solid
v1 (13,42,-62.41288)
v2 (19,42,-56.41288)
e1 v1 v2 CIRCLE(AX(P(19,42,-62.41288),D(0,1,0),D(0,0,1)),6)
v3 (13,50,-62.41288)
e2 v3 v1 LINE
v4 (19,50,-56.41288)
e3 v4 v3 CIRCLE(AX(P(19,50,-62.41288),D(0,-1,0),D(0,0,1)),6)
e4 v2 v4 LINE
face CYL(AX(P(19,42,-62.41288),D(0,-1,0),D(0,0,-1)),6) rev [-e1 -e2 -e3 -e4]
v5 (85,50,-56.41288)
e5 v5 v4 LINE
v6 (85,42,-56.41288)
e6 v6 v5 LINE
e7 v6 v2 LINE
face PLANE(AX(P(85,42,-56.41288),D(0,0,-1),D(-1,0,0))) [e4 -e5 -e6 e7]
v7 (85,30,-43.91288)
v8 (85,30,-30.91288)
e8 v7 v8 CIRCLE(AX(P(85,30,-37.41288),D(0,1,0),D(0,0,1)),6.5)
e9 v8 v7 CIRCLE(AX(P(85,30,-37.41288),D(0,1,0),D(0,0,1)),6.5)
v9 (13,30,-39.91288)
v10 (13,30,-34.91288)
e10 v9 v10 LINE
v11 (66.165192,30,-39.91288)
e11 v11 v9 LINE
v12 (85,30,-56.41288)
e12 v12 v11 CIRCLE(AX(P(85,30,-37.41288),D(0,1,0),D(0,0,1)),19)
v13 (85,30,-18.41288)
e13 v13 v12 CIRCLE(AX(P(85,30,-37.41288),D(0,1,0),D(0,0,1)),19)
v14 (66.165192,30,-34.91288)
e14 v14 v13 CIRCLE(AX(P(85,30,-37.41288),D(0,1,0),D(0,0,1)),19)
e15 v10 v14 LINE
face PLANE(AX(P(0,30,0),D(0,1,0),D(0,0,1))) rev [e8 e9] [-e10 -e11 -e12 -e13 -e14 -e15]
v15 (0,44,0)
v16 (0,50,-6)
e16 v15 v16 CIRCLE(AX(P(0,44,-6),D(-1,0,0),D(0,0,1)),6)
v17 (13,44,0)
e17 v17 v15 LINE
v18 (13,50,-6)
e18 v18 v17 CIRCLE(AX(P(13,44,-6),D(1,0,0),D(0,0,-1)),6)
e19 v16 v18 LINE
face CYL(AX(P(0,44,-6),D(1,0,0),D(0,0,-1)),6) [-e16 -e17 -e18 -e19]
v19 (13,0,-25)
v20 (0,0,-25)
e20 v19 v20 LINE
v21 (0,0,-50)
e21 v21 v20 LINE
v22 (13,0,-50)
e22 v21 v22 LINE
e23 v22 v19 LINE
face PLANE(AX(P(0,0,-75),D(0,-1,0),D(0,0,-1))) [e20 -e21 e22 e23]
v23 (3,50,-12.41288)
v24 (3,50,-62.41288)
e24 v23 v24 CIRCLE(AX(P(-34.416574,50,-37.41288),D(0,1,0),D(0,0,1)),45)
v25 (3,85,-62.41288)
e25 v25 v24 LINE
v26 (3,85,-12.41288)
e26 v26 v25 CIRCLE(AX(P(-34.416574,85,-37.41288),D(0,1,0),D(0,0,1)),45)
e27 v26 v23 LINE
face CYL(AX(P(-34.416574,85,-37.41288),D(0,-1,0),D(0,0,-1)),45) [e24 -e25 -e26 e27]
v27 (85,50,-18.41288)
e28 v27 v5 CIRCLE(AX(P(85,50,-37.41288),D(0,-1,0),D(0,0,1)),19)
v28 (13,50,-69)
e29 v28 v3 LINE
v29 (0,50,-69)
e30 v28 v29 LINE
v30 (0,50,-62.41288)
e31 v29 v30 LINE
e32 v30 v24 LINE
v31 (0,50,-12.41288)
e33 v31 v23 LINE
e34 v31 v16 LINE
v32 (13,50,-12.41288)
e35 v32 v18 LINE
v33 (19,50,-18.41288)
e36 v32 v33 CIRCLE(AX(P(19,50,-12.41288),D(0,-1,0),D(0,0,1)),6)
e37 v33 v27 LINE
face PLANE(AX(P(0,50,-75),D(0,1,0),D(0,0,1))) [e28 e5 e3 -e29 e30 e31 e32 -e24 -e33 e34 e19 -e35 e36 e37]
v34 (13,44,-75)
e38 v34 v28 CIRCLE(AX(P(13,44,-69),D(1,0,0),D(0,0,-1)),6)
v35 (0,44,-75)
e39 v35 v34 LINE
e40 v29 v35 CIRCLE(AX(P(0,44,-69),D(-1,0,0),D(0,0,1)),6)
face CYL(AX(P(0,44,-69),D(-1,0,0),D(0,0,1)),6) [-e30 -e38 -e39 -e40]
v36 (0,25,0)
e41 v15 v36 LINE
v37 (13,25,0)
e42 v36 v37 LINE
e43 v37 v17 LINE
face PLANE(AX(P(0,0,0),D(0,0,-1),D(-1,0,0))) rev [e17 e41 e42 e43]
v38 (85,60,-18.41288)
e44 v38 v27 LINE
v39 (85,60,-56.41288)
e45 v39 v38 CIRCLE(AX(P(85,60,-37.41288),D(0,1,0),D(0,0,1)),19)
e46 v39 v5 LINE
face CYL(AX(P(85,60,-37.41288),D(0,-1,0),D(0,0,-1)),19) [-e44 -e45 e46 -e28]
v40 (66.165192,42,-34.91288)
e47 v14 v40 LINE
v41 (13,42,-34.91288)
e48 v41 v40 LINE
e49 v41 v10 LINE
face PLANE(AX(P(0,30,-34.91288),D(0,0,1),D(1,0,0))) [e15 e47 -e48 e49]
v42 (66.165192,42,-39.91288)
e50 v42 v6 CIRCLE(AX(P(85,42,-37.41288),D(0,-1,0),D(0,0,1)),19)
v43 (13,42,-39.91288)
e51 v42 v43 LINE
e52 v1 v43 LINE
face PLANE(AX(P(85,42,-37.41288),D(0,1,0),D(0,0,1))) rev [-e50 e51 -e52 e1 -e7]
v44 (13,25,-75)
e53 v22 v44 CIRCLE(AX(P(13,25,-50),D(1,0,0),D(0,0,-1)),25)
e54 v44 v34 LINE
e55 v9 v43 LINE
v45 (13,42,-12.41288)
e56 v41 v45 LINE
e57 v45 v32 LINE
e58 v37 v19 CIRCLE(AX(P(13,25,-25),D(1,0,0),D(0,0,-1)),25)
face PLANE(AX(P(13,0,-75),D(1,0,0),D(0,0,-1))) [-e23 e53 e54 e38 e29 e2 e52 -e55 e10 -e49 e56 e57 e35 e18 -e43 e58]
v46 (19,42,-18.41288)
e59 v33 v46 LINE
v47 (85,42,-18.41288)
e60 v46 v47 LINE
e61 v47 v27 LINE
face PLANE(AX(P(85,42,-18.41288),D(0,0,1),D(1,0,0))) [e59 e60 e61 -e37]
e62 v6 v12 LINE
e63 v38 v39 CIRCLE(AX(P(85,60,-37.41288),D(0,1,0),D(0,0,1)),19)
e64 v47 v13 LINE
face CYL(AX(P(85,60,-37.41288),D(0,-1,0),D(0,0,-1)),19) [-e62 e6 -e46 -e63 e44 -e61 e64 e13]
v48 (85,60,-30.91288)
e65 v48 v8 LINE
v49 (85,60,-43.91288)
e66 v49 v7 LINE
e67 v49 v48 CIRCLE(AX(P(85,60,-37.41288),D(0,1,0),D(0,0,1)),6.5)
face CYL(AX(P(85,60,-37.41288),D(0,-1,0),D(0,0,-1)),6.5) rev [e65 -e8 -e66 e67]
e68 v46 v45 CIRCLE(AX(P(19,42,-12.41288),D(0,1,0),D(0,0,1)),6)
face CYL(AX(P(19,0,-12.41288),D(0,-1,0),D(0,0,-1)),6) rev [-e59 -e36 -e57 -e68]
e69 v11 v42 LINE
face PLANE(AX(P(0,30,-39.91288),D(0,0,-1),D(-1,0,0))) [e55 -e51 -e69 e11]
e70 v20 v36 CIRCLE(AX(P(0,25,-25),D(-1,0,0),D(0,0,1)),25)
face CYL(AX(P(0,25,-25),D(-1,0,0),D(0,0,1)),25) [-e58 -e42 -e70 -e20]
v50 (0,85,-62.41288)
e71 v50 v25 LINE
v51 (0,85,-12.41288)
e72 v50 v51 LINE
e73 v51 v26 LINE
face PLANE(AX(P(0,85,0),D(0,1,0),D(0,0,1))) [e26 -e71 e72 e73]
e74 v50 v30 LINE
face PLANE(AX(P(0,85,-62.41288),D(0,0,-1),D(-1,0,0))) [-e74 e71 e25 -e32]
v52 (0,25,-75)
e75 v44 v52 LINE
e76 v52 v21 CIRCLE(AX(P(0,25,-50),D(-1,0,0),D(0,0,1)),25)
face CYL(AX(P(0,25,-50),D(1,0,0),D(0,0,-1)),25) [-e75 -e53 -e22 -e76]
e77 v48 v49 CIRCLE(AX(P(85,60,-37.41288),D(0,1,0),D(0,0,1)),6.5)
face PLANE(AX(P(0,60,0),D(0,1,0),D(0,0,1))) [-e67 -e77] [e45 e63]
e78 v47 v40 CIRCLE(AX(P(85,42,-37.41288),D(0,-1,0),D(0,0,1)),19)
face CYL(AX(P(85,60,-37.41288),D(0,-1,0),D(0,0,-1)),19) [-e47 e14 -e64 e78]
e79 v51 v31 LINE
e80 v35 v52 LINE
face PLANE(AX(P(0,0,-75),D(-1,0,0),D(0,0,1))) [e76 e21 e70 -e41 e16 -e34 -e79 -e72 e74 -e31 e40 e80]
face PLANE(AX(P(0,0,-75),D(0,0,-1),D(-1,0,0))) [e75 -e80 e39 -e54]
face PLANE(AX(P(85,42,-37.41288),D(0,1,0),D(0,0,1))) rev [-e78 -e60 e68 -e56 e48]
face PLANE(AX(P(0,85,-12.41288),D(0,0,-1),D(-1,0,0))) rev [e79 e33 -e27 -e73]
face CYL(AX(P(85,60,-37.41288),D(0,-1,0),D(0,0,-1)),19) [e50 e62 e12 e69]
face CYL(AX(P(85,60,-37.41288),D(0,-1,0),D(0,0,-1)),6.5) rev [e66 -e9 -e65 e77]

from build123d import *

# Parameters (mm, degrees)
BASE_BLOCK_SKETCH_W   = 13
BASE_BLOCK_SKETCH_H   = 50
BASE_BLOCK_DEPTH      = 75
BASE_END_ROUND_R25_R  = 25
BASE_EDGE_FILLET_R6_R = 6
ARM_WEB_DEPTH         = 35
HUB_BOSS_SKETCH_R     = 19
HUB_BOSS_SKETCH_R_2   = 6.5
HUB_BOSS_DEPTH        = 30
UPPER_LUG_DEPTH       = 8
CURVED_START          = -20
CURVED_BLADE_DEPTH    = 20
LUG_FILLET_R6_A_R     = 6
LUG_FILLET_R6_B_R     = 6


with BuildPart() as part:
    # Base Block Sketch → Base Block (new body)
    with BuildSketch(Plane.XY):
        with Locations((6.5, 25)):
            Rectangle(BASE_BLOCK_SKETCH_W, BASE_BLOCK_SKETCH_H)
    extrude(amount=-BASE_BLOCK_DEPTH)

    # Base End Round R25
    base_end_round_r25_edges = [part.edges().sort_by_distance(p)[0] for p in [
        (6.5, 0, 0),
        (6.5, 0, -75),
    ]]
    fillet(base_end_round_r25_edges, radius=BASE_END_ROUND_R25_R)

    # Base Edge Fillet R6
    base_edge_fillet_r6_edges = [part.edges().sort_by_distance(p)[0] for p in [
        (6.5, 50, -75),
        (6.5, 50, 0),
    ]]
    fillet(base_edge_fillet_r6_edges, radius=BASE_EDGE_FILLET_R6_R)

    # Arm Web Sketch → Arm Web (add)
    with BuildSketch(Plane(origin=(0, 50, 0), x_dir=(1, 0, 0), z_dir=(0, 1, 0))):
        with BuildLine():
            Line((3, 62.41287987), (0, 62.41287987))
            Line((0, 62.41287987), (0, 37.41287987))
            Line((0, 37.41287987), (0, 12.41287987))
            Line((0, 12.41287987), (3, 12.41287987))
            ThreePointArc((3, 12.41287987), (10.583426132, 37.41287987), (3, 62.41287987))
        make_face()
    extrude(amount=ARM_WEB_DEPTH)



with BuildPart() as body_2:
    # Hub Boss Sketch → Hub Boss (new body)
    with BuildSketch(Plane(origin=(0, 30, 0), x_dir=(1, 0, 0), z_dir=(0, 1, 0))):
        with Locations(Location((85, 37.41287987, 0), (0, 0, 270))):
            Circle(HUB_BOSS_SKETCH_R)
        with Locations(Location((85, 37.41287987, 0), (0, 0, 270))):
            Circle(HUB_BOSS_SKETCH_R_2, mode=Mode.SUBTRACT)
    extrude(amount=HUB_BOSS_DEPTH)


with BuildPart() as part_1:
    add(part.part)

    add(body_2.part)  # Upper Lug merges body 2
    # Upper Lug Sketch → Upper Lug (add)
    with BuildSketch(Plane(origin=(0, 50, 0), x_dir=(1, 0, 0), z_dir=(0, 1, 0))):
        with BuildLine():
            Line((85, 56.41287987), (13, 56.41287987))
            Line((13, 56.41287987), (13, 18.41287987))
            Line((13, 18.41287987), (85, 18.41287987))
            ThreePointArc((85, 18.41287987), (66, 37.41287987), (85, 56.41287987))
        make_face()
    extrude(amount=-UPPER_LUG_DEPTH)

    # Curved Blade Sketch → Curved Blade (add)
    with BuildSketch(Plane(origin=(0, 50, 0), x_dir=(1, 0, 0), z_dir=(0, 1, 0)).offset(CURVED_START)):
        with BuildLine():
            Line((0, 34.91287987), (66.165191798, 34.91287987))
            ThreePointArc((66.165191798, 34.91287987), (66, 37.41287987), (66.165191798, 39.91287987))
            Line((66.165191798, 39.91287987), (0, 39.91287987))
            Line((0, 39.91287987), (0, 34.91287987))
        make_face()
    extrude(amount=CURVED_BLADE_DEPTH)

    # Lug Fillet R6 A
    lug_fillet_r6_a_edges = [part_1.edges().sort_by_distance(p)[0] for p in [
        (13, 46, -18.41287987),
    ]]
    fillet(lug_fillet_r6_a_edges, radius=LUG_FILLET_R6_A_R)

    # Lug Fillet R6 B
    lug_fillet_r6_b_edges = [part_1.edges().sort_by_distance(p)[0] for p in [
        (13, 46, -56.41287987),
    ]]
    fillet(lug_fillet_r6_b_edges, radius=LUG_FILLET_R6_B_R)


solid = part_1.part
